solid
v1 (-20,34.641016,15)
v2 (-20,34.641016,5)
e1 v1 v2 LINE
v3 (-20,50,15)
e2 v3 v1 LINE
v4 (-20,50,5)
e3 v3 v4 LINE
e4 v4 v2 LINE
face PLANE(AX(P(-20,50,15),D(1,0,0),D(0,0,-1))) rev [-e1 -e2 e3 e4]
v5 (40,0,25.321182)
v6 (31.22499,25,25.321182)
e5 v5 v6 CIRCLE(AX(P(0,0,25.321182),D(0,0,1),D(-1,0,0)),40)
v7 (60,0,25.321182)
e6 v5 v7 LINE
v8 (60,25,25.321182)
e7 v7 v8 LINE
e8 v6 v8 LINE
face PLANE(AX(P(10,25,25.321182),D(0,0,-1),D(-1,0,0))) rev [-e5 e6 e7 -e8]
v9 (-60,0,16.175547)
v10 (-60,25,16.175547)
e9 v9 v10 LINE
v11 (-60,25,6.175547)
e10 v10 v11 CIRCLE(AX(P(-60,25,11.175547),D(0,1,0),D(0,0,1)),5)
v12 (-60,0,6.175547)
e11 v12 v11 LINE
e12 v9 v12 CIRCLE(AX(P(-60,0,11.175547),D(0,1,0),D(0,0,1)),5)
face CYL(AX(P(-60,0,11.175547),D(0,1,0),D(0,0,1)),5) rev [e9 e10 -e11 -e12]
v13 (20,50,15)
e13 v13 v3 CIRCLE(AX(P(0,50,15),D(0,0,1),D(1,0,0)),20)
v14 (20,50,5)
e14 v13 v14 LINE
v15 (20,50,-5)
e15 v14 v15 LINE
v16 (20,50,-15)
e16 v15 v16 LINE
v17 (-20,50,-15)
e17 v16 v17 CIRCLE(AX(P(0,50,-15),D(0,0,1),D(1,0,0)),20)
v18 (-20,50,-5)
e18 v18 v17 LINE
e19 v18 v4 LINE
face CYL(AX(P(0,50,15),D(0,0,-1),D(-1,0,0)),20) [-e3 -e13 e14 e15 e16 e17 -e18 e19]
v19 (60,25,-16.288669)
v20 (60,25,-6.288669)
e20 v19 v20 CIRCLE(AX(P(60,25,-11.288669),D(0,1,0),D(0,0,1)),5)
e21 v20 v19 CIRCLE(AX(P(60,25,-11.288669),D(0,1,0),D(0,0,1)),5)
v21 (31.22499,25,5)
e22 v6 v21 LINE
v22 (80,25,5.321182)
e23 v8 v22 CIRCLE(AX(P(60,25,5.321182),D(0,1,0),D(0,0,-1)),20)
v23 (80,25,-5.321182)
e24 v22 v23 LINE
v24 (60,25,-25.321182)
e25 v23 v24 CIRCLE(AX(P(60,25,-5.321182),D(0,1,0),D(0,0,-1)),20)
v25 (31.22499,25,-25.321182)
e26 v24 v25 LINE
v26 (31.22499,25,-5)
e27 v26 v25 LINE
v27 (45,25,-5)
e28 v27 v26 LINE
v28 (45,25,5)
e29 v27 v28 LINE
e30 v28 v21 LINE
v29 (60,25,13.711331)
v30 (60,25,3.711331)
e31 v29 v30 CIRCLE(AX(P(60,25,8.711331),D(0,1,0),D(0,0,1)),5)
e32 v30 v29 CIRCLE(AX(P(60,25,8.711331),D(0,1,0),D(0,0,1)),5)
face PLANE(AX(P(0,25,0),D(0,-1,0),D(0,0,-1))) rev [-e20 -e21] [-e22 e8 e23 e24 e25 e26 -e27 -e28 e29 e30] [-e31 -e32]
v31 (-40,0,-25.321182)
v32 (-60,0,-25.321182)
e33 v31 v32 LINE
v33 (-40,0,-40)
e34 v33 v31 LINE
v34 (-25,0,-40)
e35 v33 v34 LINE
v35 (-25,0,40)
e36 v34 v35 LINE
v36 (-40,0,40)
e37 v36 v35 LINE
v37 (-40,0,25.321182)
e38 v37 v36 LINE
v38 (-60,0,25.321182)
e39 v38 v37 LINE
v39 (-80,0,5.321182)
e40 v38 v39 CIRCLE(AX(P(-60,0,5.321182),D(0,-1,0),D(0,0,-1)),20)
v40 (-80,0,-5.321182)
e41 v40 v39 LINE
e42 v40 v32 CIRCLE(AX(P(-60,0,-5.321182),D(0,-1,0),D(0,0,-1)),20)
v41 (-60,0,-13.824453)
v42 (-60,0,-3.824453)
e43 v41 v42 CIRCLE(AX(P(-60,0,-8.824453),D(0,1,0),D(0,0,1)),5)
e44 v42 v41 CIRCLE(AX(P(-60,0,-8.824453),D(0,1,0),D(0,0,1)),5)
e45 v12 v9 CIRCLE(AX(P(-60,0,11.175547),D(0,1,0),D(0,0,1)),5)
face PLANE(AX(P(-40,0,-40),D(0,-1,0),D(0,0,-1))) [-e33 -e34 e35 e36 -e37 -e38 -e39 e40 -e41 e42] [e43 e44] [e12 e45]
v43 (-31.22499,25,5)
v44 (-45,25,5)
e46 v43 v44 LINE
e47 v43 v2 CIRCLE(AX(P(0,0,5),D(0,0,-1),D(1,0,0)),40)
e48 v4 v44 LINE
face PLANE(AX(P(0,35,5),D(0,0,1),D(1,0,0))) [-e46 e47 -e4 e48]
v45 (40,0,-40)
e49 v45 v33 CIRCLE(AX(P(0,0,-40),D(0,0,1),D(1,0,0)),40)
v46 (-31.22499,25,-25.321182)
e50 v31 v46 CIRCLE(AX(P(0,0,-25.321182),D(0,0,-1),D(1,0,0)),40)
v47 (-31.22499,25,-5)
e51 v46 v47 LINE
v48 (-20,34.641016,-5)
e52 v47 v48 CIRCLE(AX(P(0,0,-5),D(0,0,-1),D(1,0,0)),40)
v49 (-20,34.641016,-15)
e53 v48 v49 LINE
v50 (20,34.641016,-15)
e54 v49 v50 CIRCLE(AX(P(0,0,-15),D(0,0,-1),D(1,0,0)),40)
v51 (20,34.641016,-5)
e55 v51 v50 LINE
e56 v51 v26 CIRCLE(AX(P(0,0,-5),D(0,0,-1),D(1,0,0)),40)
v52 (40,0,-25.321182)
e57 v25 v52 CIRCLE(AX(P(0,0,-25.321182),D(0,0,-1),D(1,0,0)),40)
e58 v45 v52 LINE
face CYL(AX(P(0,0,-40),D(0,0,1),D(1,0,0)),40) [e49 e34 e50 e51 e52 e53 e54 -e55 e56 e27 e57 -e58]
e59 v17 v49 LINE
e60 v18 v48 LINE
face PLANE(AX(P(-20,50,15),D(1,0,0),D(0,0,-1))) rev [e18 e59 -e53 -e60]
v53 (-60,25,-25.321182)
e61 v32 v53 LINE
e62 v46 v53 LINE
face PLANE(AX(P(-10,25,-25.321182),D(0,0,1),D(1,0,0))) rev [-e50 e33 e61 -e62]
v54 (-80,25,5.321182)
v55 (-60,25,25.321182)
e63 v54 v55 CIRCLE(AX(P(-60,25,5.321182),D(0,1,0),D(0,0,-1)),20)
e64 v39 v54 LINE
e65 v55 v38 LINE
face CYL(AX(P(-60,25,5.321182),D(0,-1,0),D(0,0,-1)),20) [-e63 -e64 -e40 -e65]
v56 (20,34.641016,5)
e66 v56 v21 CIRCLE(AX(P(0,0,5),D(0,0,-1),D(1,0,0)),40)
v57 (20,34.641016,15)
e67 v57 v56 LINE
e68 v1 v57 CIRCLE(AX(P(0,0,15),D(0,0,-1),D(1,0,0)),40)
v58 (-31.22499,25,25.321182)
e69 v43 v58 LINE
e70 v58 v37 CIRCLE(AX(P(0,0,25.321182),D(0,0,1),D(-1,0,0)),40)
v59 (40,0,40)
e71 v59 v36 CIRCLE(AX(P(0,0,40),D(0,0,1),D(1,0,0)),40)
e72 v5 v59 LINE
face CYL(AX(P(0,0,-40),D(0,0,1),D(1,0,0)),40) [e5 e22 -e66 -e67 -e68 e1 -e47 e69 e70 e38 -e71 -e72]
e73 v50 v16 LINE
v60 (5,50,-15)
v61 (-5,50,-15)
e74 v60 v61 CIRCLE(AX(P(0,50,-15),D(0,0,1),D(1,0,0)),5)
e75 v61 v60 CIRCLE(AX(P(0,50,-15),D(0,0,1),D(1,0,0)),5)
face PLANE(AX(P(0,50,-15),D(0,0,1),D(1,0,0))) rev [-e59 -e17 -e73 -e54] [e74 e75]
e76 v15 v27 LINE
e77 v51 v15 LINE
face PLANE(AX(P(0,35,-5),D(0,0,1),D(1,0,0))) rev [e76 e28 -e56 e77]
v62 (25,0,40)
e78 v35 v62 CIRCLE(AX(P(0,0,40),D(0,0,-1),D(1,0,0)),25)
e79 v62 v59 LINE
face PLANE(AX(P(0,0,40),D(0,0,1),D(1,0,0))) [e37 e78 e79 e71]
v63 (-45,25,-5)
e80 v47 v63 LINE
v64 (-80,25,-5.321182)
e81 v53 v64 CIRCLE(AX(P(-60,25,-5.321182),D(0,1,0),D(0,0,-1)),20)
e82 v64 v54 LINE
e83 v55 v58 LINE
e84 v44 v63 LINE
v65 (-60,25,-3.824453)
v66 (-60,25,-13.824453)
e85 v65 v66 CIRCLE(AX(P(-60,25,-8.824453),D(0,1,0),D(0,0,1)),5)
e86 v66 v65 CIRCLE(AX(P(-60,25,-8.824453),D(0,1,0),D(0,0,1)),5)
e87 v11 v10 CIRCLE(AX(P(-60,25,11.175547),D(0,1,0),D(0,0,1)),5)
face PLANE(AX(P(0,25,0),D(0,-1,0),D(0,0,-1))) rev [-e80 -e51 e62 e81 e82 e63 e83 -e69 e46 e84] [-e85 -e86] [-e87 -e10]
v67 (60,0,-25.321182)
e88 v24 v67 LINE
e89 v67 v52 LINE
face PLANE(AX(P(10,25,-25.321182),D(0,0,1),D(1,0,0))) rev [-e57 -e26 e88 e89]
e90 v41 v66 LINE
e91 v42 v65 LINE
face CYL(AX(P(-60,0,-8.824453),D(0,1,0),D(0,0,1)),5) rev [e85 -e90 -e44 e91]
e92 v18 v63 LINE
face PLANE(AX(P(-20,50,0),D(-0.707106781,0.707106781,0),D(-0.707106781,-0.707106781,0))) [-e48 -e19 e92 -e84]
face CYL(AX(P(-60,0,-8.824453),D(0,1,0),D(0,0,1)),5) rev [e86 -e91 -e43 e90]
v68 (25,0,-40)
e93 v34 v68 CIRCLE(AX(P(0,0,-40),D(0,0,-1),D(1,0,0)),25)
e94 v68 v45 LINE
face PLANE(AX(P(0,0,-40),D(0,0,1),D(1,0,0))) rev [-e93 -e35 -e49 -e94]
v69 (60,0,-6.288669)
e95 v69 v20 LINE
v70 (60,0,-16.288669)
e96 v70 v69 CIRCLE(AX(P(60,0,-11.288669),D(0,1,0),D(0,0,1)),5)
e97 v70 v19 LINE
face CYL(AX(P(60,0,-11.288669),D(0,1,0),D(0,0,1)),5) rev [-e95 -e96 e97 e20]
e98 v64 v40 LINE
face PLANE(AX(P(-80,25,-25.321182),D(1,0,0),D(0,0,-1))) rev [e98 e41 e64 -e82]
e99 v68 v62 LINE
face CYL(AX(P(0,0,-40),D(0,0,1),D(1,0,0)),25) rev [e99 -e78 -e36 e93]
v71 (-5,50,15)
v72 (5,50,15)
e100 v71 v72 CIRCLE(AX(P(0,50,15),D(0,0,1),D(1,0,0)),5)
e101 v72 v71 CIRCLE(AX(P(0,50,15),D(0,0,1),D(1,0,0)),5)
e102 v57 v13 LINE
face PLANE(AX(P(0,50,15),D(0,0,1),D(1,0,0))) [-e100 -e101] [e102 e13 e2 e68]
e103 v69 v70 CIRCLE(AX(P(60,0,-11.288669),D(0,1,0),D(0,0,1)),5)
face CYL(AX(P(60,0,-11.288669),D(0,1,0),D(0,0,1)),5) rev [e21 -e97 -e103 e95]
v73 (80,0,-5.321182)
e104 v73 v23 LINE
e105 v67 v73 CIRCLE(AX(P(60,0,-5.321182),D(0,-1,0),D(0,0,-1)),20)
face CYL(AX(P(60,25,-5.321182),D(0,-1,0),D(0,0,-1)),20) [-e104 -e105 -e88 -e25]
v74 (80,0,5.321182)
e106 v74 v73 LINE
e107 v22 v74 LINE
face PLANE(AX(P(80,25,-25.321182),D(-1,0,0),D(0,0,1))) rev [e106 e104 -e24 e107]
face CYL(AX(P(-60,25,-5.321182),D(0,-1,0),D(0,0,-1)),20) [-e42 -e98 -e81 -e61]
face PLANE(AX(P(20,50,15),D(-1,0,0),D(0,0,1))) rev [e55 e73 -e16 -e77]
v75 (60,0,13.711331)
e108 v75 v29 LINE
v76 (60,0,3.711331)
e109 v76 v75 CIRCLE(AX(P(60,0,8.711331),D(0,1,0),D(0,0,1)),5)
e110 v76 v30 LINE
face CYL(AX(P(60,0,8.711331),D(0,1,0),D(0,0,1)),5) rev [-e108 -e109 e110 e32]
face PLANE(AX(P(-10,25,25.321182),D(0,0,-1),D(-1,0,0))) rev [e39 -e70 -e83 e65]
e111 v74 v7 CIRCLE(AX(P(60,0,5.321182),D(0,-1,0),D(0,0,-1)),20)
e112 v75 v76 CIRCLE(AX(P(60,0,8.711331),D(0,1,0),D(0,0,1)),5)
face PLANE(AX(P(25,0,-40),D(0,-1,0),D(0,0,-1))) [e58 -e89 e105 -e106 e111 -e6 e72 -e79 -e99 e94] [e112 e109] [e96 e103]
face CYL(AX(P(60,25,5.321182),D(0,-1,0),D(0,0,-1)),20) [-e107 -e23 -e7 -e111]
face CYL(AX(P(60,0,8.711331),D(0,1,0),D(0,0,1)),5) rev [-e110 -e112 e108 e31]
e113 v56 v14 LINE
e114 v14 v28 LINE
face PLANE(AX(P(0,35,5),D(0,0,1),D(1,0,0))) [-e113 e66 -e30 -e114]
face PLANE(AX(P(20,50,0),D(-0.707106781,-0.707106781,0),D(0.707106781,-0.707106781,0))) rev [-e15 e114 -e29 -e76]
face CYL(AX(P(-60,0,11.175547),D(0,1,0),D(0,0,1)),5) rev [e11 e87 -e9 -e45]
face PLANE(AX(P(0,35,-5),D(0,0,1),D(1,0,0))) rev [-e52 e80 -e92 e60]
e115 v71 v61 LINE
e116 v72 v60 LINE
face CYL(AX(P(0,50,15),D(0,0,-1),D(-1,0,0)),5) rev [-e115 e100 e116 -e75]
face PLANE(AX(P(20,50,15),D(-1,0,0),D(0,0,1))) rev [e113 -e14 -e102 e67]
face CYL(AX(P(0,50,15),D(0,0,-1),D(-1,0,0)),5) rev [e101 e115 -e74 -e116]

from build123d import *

# Parameters (mm, degrees)
HOUSING_BLOCK_DEPTH           = 40
TOP_LUG_SKETCH_R              = 5
TOP_LUG_DEPTH                 = 15
BASE_FLANGE_SKETCH_W          = 70
BASE_FLANGE_SKETCH_H          = 50.64236497
BASE_FLANGE_DEPTH             = 25
BEARING_SEAT_CUT_DEPTH        = 80
FLANGE_END_ROUND_R20_A_R      = 20
FLANGE_END_ROUND_R20_B_R      = 20
MOUNTING_HOLES_SET_1_SKETCH_R = 5
MOUNTING_HOLES_SET_1_DEPTH    = 25
MOUNTING_HOLES_SET_2_SKETCH_R = 5
MOUNTING_HOLES_SET_2_DEPTH    = 25
SUPPORT_RIB_1_REACH           = 115.578
SUPPORT_RIB_1_SKETCH_WALL_W   = 264.511672892
SUPPORT_RIB_1_SKETCH_WALL_H   = 10
SUPPORT_RIB_2_REACH           = 115.578
SUPPORT_RIB_2_SKETCH_WALL_W   = 264.511672892
SUPPORT_RIB_2_SKETCH_WALL_H   = 10


with BuildPart() as part:
    # Housing Block Sketch → Housing Block (new, symmetric)
    with BuildSketch(Plane.XY):
        with BuildLine():
            Line((-40, 0), (-25, 0))
            ThreePointArc((-25, 0), (0, 25), (25, 0))
            Line((25, 0), (40, 0))
            ThreePointArc((40, 0), (0, 40), (-40, 0))
        make_face()
    extrude(amount=HOUSING_BLOCK_DEPTH, both=True)

    # Top Lug Sketch → Top Lug (add, symmetric)
    with BuildSketch(Plane.XY):
        with BuildLine():
            Line((-20, 50), (-20, 34.002392221))
            Line((-20, 34.002392221), (20, 34.641016151))
            Line((20, 34.641016151), (20, 50))
            ThreePointArc((20, 50), (0, 70), (-20, 50))
        make_face()
        with Locations((0, 50)):
            Circle(TOP_LUG_SKETCH_R, mode=Mode.SUBTRACT)
    extrude(amount=TOP_LUG_DEPTH, both=True)

    # Base Flange Sketch → Base Flange (add)
    with BuildSketch(Plane(origin=(0, 0, 0), x_dir=(1, 0, 0), z_dir=(0, 1, 0))):
        with Locations((45, 0)):
            Rectangle(BASE_FLANGE_SKETCH_W, BASE_FLANGE_SKETCH_H)
        with Locations((-45, 0)):
            Rectangle(BASE_FLANGE_SKETCH_W, BASE_FLANGE_SKETCH_H)
    extrude(amount=BASE_FLANGE_DEPTH)

    # Bearing Seat Sketch → Bearing Seat Cut (cut)
    with BuildSketch(Plane.XY.offset(25.321182485)):
        with BuildLine():
            Line((-10, 22.912878475), (-10, 0))
            Line((-10, 0), (-25, 0))
            ThreePointArc((-25, 0), (-20.916500663, 13.693063938), (-10, 22.912878475))
        make_face()
        with BuildLine():
            Line((10, 22.912878475), (10, 0))
            Line((10, 0), (25, 0))
            ThreePointArc((25, 0), (20.916500663, 13.693063938), (10, 22.912878475))
        make_face()
    extrude(amount=-BEARING_SEAT_CUT_DEPTH, mode=Mode.SUBTRACT)

    # Flange End Round R20 A
    flange_end_round_r20_a_edges = [part.edges().sort_by_distance(p)[0] for p in [
        (80, 12.5, -25.321182485),
        (80, 12.5, 25.321182485),
        (-80, 12.5, 25.321182485),
    ]]
    fillet(flange_end_round_r20_a_edges, radius=FLANGE_END_ROUND_R20_A_R)

    # Flange End Round R20 B
    flange_end_round_r20_b_edges = [part.edges().sort_by_distance(p)[0] for p in [
        (-80, 12.5, -25.321182485),
    ]]
    fillet(flange_end_round_r20_b_edges, radius=FLANGE_END_ROUND_R20_B_R)

    # Mounting Holes Set 1 Sketch → Mounting Holes Set 1 (cut)
    with BuildSketch(Plane(origin=(0, 25, 0), x_dir=(1, 0, 0), z_dir=(0, 1, 0))):
        with Locations(Location((-60, 8.824452572, 0), (0, 0, 270))):
            Circle(MOUNTING_HOLES_SET_1_SKETCH_R)
        with Locations(Location((-60, -11.175547428, 0), (0, 0, 270))):
            Circle(MOUNTING_HOLES_SET_1_SKETCH_R)
    extrude(amount=-MOUNTING_HOLES_SET_1_DEPTH, mode=Mode.SUBTRACT)

    # Mounting Holes Set 2 Sketch → Mounting Holes Set 2 (cut)
    with BuildSketch(Plane(origin=(0, 25, 0), x_dir=(1, 0, 0), z_dir=(0, 1, 0))):
        with Locations(Location((60, 11.288668944, 0), (0, 0, 270))):
            Circle(MOUNTING_HOLES_SET_2_SKETCH_R)
        with Locations(Location((60, -8.711331056, 0), (0, 0, 270))):
            Circle(MOUNTING_HOLES_SET_2_SKETCH_R)
    extrude(amount=-MOUNTING_HOLES_SET_2_DEPTH, mode=Mode.SUBTRACT)

    # Support Rib 1 Sketch wall → Support Rib 1 (add, up to next)
    with BuildSketch(Plane(origin=(-32.5, 37.5, 0), x_dir=(-0.707106781187, -0.707106781187, 0), z_dir=(0.707106781187, -0.707106781187, 0)), mode=Mode.PRIVATE) as support_rib_1_sk1:
        Rectangle(SUPPORT_RIB_1_SKETCH_WALL_W, SUPPORT_RIB_1_SKETCH_WALL_H)
    support_rib_1_tool1 = extrude(support_rib_1_sk1.sketch, amount=SUPPORT_RIB_1_REACH, mode=Mode.PRIVATE) - part.part
    add(support_rib_1_tool1.solids().sort_by_distance((-32.5, 37.5, 0))[0])

    # Support Rib 2 Sketch wall → Support Rib 2 (add, up to next)
    with BuildSketch(Plane(origin=(32.5, 37.5, 0), x_dir=(0.707106781187, -0.707106781187, 0), z_dir=(0.707106781187, 0.707106781187, 0)), mode=Mode.PRIVATE) as support_rib_2_sk1:
        Rectangle(SUPPORT_RIB_2_SKETCH_WALL_W, SUPPORT_RIB_2_SKETCH_WALL_H)
    support_rib_2_tool1 = extrude(support_rib_2_sk1.sketch, amount=-SUPPORT_RIB_2_REACH, mode=Mode.PRIVATE) - part.part
    add(support_rib_2_tool1.solids().sort_by_distance((32.5, 37.5, 0))[0])


solid = part.part
